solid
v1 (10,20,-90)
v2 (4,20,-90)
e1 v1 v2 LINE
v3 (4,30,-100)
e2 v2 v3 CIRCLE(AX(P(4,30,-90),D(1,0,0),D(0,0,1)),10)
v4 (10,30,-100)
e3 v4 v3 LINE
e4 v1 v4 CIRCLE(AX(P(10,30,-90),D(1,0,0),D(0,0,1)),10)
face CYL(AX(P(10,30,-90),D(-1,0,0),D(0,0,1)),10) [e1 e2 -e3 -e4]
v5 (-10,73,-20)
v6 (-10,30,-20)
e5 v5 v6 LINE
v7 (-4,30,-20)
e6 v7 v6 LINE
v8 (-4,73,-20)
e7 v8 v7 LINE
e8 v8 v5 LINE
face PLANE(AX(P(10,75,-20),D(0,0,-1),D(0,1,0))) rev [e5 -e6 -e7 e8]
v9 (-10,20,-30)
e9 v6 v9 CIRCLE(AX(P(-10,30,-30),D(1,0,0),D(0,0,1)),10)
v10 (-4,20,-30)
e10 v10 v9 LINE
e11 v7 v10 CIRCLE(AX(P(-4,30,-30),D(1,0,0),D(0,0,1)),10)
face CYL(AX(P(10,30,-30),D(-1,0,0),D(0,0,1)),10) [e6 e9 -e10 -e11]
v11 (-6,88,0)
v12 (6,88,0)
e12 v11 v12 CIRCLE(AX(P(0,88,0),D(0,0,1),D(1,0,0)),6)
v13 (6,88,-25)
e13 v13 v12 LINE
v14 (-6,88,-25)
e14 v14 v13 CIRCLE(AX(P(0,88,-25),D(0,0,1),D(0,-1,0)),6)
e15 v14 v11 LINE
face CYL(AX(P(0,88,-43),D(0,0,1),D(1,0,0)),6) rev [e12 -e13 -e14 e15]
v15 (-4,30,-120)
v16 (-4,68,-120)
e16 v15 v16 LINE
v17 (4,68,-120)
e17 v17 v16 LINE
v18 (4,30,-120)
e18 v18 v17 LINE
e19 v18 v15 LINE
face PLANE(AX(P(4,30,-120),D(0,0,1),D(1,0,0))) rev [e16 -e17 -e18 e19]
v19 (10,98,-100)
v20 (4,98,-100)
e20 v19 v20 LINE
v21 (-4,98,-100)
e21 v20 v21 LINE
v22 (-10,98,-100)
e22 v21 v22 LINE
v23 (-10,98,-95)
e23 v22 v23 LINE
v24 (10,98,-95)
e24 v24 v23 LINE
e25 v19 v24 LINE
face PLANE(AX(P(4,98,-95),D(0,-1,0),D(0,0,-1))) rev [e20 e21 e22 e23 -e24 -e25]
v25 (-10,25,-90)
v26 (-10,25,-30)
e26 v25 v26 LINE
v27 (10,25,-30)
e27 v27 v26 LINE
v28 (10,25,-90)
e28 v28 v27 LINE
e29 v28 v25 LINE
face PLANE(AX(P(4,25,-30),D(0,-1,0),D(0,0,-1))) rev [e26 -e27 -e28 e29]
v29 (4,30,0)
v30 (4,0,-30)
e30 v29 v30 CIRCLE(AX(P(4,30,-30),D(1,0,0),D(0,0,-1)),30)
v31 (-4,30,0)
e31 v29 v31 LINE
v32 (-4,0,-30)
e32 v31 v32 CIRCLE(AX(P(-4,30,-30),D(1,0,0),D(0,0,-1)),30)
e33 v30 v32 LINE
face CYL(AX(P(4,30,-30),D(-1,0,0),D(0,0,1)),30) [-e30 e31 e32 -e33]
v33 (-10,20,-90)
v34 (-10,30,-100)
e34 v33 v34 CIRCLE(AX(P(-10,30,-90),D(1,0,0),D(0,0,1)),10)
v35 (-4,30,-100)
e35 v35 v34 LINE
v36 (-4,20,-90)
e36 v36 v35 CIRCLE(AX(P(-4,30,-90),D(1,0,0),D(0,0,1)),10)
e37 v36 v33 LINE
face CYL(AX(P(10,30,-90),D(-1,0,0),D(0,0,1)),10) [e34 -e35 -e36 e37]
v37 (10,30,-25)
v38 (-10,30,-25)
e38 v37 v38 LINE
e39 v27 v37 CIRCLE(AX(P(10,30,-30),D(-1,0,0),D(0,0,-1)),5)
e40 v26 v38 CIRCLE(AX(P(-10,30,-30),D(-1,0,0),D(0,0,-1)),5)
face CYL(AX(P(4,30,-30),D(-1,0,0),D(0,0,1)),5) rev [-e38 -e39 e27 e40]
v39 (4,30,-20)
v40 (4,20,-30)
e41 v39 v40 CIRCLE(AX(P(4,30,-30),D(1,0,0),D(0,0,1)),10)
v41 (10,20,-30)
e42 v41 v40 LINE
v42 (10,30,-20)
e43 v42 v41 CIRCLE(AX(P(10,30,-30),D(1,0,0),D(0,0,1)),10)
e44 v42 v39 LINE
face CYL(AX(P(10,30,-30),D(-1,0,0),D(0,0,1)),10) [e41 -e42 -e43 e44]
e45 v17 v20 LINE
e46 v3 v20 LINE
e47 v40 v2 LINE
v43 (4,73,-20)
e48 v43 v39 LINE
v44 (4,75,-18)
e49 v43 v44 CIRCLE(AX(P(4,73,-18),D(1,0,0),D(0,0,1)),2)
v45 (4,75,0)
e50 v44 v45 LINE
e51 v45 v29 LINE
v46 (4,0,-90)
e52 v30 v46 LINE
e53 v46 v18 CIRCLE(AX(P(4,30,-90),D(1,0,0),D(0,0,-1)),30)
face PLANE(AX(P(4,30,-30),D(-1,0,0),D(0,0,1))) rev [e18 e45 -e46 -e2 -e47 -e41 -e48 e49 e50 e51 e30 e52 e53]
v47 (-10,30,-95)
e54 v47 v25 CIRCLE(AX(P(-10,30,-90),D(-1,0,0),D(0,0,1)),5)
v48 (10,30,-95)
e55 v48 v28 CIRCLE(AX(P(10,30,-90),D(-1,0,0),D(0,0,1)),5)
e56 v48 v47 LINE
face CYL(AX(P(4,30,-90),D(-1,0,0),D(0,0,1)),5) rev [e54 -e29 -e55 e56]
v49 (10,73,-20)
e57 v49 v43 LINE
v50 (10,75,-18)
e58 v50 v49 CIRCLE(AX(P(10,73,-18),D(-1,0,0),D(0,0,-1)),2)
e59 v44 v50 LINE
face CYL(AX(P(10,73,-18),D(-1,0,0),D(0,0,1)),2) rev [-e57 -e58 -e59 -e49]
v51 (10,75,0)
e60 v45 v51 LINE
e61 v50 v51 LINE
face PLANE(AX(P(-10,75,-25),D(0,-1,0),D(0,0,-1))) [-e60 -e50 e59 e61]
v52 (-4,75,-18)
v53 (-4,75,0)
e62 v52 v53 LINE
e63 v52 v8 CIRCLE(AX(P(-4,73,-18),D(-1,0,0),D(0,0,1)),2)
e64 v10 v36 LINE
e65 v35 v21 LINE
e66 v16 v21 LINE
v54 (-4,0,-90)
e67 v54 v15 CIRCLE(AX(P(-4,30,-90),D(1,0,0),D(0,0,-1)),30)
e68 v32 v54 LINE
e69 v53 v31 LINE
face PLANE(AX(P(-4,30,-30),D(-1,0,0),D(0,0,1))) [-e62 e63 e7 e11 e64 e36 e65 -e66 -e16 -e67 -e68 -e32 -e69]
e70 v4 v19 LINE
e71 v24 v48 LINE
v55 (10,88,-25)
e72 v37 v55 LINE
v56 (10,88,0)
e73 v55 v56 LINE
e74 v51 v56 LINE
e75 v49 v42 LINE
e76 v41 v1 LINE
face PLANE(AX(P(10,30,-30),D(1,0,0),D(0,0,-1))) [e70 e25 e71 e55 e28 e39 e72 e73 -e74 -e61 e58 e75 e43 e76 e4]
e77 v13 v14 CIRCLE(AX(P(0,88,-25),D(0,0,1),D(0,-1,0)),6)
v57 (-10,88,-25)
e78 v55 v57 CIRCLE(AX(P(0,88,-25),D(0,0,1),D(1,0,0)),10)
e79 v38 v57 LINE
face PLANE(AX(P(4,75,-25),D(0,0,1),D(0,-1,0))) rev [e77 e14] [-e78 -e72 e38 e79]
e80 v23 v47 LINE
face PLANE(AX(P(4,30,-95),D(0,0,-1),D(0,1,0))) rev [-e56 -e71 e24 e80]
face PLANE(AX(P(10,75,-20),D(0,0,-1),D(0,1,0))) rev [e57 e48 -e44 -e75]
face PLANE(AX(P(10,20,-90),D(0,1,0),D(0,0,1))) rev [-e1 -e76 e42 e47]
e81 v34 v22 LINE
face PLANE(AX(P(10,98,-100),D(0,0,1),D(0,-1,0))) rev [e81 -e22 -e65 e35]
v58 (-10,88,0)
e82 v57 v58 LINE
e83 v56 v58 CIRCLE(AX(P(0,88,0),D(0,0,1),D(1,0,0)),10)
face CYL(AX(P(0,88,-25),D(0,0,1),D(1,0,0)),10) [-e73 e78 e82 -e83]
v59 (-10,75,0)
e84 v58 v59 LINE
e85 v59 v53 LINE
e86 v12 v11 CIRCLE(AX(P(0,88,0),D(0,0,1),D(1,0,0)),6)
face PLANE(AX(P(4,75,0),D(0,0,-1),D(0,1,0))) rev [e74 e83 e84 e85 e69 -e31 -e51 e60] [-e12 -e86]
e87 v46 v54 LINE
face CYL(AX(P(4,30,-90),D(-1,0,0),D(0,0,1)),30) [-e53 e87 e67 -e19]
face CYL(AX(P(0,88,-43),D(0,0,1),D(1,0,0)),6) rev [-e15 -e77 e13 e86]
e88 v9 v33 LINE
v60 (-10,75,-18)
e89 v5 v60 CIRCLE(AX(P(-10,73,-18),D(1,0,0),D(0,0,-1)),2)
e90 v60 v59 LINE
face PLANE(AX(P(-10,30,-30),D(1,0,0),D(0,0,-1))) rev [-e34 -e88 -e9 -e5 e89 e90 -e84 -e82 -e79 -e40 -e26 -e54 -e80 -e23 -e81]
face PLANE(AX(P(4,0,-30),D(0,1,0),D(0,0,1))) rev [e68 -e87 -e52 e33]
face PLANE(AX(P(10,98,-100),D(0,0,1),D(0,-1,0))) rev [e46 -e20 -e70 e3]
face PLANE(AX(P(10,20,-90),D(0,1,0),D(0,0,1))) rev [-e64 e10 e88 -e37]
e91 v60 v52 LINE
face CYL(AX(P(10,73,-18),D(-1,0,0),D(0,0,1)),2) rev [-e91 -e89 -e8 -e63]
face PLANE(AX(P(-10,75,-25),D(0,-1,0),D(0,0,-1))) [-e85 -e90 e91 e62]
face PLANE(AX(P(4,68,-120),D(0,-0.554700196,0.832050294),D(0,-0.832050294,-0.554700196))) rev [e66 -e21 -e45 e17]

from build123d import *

# Parameters (mm, degrees)
C_FRAME_BODY_DEPTH  = 4
FRAME_RIM_DEPTH     = 10
SCREW_BOSS_DEPTH    = 25
SCREW_BORE_SKETCH_R = 6
SCREW_BORE_12_DEPTH = 43
EDGE_FILLETS_R2_R   = 2


with BuildPart() as part:
    # C-Frame Profile Sketch → C-Frame Body (new, symmetric)
    with BuildSketch(Plane(origin=(0, 0, 0), x_dir=(0, 0, -1), z_dir=(1, 0, 0))):
        with BuildLine():
            Line((0, 75), (0, 30))
            ThreePointArc((0, 30), (8.786796564, 8.786796564), (30, 0))
            Line((30, 0), (90, 0))
            ThreePointArc((90, 0), (111.213203436, 8.786796564), (120, 30))
            Line((120, 30), (120, 68))
            Line((120, 68), (100, 98))
            Line((100, 98), (95, 98))
            Line((95, 98), (95, 30))
            ThreePointArc((95, 30), (93.535533906, 26.464466094), (90, 25))
            Line((90, 25), (30, 25))
            ThreePointArc((30, 25), (26.464466094, 26.464466094), (25, 30))
            Line((25, 30), (25, 75))
            Line((25, 75), (0, 75))
        make_face()
    extrude(amount=C_FRAME_BODY_DEPTH, both=True)

    # Frame Rim Sketch → Frame Rim (add, symmetric)
    with BuildSketch(Plane(origin=(0, 0, 0), x_dir=(0, 0, -1), z_dir=(1, 0, 0))):
        with BuildLine():
            Line((25, 75), (20, 75))
            Line((20, 75), (20, 30))
            ThreePointArc((20, 30), (22.928932188, 22.928932188), (30, 20))
            Line((30, 20), (90, 20))
            ThreePointArc((90, 20), (97.071067812, 22.928932188), (100, 30))
            Line((100, 30), (100, 98))
            Line((100, 98), (95, 98))
            Line((95, 98), (95, 30))
            ThreePointArc((95, 30), (93.535533906, 26.464466094), (90, 25))
            Line((90, 25), (30, 25))
            ThreePointArc((30, 25), (26.464466094, 26.464466094), (25, 30))
            Line((25, 30), (25, 75))
        make_face()
    extrude(amount=FRAME_RIM_DEPTH, both=True)

    # Screw Boss Sketch → Screw Boss (add)
    with BuildSketch(Plane.XY):
        with BuildLine():
            Line((-10, 75), (10, 75))
            Line((10, 75), (10, 88))
            ThreePointArc((10, 88), (0, 98), (-10, 88))
            Line((-10, 88), (-10, 75))
        make_face()
    extrude(amount=-SCREW_BOSS_DEPTH)

    # Screw Bore Sketch → Screw Bore Ø12 (cut)
    with BuildSketch(Plane.XY):
        with Locations((0, 88)):
            Circle(SCREW_BORE_SKETCH_R)
    extrude(amount=-SCREW_BORE_12_DEPTH, mode=Mode.SUBTRACT)

    # Edge Fillets R2
    edge_fillets_r2_edges = [part.edges().sort_by_distance(p)[0] for p in [
        (7, 75, -20),
        (-7, 75, -20),
    ]]
    fillet(edge_fillets_r2_edges, radius=EDGE_FILLETS_R2_R)


solid = part.part
